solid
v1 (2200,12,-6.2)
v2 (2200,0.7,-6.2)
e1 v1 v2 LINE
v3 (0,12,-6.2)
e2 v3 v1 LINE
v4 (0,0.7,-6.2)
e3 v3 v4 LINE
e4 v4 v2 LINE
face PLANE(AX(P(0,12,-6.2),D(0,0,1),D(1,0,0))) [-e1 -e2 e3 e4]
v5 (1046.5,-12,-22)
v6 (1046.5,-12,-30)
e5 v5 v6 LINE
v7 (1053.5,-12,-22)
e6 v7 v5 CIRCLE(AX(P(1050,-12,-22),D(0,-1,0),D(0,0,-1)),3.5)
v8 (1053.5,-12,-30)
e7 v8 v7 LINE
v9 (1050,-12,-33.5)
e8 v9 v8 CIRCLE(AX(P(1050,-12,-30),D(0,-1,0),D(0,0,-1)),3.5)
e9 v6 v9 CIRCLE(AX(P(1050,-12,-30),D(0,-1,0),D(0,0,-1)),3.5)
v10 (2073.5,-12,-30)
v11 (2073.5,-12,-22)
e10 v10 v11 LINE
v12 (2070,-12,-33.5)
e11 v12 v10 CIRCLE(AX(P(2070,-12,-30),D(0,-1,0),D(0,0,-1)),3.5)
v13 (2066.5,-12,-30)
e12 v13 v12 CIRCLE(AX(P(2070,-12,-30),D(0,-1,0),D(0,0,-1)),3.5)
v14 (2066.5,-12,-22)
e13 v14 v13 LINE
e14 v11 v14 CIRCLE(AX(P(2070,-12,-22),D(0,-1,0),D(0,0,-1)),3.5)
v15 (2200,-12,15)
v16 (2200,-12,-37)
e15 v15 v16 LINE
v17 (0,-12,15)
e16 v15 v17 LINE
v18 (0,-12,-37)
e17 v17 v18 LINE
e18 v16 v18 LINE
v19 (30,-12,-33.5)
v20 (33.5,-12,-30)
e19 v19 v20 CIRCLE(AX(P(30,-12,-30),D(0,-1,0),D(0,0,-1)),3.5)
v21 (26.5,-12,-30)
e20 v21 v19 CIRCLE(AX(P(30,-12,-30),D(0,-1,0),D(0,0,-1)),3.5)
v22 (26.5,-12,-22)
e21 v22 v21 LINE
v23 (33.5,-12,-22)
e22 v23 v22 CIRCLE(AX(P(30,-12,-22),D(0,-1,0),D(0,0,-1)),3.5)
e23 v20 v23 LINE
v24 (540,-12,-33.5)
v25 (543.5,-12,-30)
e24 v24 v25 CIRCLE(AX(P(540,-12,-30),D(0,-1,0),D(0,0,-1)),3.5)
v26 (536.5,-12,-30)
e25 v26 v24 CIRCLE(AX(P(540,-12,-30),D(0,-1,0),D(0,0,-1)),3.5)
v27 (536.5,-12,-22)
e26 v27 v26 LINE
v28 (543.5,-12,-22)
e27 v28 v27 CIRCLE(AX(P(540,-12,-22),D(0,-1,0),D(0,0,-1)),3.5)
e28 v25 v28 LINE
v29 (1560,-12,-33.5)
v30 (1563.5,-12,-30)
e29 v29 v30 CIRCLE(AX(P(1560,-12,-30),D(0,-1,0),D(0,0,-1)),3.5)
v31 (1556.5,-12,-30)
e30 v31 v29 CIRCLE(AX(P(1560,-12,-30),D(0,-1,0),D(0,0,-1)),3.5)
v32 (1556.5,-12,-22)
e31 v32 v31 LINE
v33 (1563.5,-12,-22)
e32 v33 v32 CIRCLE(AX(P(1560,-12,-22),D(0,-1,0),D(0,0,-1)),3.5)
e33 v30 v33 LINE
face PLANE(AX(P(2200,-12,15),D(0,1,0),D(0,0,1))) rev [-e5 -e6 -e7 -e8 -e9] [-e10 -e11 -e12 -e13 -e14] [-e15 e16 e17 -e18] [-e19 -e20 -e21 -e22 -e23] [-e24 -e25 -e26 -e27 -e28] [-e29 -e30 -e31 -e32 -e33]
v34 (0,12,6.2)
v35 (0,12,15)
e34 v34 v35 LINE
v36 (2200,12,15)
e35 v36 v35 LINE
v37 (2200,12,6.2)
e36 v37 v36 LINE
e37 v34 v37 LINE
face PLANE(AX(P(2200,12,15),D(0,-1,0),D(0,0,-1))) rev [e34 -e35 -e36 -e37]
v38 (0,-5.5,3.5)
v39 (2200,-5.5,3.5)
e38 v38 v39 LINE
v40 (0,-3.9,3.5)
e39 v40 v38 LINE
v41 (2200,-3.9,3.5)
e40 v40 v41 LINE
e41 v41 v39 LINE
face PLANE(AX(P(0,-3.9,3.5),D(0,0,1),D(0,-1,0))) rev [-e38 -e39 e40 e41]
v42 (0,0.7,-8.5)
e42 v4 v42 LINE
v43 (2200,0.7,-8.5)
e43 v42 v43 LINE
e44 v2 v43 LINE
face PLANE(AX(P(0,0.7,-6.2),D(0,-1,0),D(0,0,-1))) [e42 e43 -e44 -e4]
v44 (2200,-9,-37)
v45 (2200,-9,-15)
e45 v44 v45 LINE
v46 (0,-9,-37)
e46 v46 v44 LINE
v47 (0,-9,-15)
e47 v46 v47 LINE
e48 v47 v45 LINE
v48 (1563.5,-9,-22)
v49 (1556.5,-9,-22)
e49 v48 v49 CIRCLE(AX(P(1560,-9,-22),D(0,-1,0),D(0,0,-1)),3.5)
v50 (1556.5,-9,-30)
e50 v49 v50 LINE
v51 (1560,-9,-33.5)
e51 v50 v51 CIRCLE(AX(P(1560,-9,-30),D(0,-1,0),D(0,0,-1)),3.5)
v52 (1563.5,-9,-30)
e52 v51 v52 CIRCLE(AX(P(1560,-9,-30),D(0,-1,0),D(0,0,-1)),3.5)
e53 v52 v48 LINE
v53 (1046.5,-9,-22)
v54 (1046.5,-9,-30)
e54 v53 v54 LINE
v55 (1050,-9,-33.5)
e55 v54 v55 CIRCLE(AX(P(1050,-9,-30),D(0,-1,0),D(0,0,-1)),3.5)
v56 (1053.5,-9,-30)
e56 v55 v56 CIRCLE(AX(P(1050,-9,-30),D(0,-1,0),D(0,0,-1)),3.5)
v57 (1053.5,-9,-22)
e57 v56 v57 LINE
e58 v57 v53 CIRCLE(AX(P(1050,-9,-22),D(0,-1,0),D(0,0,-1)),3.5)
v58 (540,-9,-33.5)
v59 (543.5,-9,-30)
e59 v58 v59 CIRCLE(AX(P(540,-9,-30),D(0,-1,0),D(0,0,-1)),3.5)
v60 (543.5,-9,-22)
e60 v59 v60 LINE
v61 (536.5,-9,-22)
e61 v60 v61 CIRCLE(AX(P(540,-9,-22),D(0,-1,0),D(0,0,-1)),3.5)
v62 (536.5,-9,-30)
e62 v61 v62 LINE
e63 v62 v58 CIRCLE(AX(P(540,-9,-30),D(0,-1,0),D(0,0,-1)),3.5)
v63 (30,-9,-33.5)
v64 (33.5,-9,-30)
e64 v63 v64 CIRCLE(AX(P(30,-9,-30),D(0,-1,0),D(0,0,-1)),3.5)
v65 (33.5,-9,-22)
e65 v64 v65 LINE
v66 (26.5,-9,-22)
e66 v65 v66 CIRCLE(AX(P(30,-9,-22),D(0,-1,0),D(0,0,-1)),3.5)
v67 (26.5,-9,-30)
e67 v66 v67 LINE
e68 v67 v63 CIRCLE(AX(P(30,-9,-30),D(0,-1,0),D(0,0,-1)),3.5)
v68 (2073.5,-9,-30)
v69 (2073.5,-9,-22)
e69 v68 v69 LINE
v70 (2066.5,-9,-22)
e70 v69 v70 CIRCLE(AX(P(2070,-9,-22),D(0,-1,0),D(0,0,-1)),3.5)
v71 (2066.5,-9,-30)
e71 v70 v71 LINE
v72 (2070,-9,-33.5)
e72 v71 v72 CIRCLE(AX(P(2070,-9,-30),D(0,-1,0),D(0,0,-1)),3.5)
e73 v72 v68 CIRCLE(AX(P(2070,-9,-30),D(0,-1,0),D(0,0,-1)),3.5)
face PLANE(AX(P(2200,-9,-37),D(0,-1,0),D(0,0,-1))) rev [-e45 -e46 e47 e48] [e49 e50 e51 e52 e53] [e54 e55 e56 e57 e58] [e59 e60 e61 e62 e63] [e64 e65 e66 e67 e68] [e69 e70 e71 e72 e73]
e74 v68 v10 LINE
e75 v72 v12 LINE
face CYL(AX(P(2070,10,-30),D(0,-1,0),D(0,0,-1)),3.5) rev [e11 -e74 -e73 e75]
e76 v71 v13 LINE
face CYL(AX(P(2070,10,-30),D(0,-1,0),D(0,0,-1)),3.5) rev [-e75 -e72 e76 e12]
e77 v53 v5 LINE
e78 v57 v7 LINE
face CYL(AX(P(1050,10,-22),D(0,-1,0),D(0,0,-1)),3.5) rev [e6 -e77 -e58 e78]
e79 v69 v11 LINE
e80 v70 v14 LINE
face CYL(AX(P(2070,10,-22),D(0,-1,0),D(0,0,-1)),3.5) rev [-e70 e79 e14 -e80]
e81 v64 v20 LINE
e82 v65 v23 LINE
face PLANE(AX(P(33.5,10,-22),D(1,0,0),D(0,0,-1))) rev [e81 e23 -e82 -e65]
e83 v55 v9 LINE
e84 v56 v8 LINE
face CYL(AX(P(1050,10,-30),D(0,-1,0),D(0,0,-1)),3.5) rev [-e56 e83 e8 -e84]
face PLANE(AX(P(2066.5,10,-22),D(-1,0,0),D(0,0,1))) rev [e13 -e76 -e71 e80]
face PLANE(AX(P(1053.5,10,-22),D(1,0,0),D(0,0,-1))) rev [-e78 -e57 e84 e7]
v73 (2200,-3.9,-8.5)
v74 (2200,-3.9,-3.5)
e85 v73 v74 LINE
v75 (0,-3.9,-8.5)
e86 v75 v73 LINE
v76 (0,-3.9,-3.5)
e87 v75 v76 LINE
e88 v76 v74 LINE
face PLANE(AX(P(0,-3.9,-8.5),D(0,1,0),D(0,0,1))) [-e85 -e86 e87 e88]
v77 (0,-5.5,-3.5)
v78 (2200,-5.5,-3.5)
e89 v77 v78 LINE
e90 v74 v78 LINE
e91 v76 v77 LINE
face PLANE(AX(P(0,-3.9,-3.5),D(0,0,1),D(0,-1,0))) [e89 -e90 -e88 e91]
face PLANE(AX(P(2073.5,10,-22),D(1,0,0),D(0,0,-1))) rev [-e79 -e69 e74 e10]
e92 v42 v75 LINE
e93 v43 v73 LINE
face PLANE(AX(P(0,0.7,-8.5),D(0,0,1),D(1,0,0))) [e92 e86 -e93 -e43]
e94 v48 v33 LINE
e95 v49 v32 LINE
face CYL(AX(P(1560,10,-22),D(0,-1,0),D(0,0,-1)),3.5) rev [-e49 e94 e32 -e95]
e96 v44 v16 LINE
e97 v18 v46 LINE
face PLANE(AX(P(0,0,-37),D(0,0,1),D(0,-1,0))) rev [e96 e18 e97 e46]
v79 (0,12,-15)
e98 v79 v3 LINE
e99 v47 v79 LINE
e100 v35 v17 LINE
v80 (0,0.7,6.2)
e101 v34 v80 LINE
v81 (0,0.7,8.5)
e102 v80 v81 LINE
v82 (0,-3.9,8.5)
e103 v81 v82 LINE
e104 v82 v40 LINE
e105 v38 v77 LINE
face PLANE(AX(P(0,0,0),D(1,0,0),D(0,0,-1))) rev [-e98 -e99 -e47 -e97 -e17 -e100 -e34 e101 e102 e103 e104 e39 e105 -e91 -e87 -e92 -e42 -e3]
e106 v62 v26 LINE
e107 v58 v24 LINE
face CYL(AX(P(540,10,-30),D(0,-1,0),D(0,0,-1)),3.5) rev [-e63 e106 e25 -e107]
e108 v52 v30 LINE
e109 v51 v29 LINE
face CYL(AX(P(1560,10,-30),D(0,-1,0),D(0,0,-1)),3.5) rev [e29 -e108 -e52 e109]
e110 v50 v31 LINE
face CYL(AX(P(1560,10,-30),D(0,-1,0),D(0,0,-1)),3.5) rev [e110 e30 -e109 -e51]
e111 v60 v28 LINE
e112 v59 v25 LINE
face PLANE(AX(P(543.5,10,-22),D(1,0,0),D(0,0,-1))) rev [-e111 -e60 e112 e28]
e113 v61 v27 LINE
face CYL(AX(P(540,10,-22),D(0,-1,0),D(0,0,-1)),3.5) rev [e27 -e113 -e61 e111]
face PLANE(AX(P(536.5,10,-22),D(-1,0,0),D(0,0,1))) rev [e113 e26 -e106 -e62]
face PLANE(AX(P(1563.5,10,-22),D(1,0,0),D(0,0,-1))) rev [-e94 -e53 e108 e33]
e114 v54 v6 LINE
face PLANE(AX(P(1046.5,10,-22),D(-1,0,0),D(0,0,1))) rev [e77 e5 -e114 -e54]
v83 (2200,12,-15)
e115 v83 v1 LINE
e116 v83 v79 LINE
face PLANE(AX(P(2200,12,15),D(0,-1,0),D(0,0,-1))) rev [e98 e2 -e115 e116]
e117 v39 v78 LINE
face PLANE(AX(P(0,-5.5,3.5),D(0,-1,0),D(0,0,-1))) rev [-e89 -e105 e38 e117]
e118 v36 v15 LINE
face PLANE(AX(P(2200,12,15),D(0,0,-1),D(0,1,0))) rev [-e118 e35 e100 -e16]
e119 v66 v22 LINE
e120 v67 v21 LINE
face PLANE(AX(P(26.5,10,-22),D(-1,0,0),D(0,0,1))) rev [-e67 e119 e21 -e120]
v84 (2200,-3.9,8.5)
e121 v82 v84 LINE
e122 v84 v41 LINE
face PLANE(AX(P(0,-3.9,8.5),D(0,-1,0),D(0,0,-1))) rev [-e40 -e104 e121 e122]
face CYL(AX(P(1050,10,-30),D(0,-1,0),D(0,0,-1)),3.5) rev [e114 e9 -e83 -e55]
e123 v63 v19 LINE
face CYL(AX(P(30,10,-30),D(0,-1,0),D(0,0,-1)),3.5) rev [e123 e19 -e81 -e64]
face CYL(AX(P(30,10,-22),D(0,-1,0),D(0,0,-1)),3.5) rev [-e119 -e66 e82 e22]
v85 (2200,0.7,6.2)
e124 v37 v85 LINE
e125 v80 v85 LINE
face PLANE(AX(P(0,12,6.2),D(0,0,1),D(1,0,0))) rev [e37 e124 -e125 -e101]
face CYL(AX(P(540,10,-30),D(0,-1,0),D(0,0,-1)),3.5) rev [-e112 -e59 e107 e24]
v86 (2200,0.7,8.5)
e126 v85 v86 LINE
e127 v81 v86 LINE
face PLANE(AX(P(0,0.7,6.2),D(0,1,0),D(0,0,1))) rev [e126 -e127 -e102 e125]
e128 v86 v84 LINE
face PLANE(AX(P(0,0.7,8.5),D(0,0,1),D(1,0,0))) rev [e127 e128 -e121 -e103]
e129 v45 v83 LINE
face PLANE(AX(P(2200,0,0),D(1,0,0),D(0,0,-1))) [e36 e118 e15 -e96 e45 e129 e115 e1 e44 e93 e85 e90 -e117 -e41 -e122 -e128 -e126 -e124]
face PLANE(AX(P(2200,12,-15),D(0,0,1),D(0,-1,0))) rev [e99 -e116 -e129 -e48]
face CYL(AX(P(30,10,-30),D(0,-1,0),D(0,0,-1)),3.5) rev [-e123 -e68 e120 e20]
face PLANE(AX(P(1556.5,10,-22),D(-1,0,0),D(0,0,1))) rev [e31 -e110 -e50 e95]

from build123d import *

# Parameters (mm, degrees)
SKETCH_1_W             = 30
SKETCH_1_H             = 24
EXTRUDE_1_DEPTH        = 2200
CUT_EXTRUDE_1_DEPTH    = 2201.083862038
SKETCH_5_W             = 2200
SKETCH_5_H             = 3
EXTRUDE_2_DEPTH        = 22
CUT_EXTRUDE_2_DEPTH    = 22
PATTERN_LINEAR_1_COUNT = 6
PATTERN_LINEAR_1_PITCH = 510


with BuildPart() as part:
    # 草图1 → 凸台-拉伸1 (new body)
    with BuildSketch(Plane(origin=(0, 0, 0), x_dir=(0, 0, -1), z_dir=(1, 0, 0))):
        Rectangle(SKETCH_1_W, SKETCH_1_H)
    extrude(amount=EXTRUDE_1_DEPTH)

    # 草图2 → 切除-拉伸1 (cut, through all)
    with BuildSketch(Plane(origin=(2200, 0, 0), x_dir=(0, 0, -1), z_dir=(1, 0, 0))):
        Polygon((-6.2, 12), (-6.2, 0.7), (-8.5, 0.7), (-8.5, -3.9), (-3.5, -3.9), (-3.5, -5.5), (3.5, -5.5), (3.5, -3.9), (8.5, -3.9), (8.5, 0.7), (6.2, 0.7), (6.2, 12), align=None)
    extrude(amount=-CUT_EXTRUDE_1_DEPTH, mode=Mode.SUBTRACT)

    # 草图5 → 凸台-拉伸2 (add)
    with BuildSketch(Plane(origin=(0, 0, -15), x_dir=(-1, 0, 0), z_dir=(0, 0, -1))):
        with Locations((-1100, -10.5)):
            Rectangle(SKETCH_5_W, SKETCH_5_H)
    extrude(amount=EXTRUDE_2_DEPTH)

    # 草图6 → 切除-拉伸2 (cut)
    with BuildSketch(Plane.XZ.offset(12)):
        with BuildLine():
            Line((33.5, -22), (33.5, -30))
            ThreePointArc((33.5, -30), (30, -33.5), (26.5, -30))
            Line((26.5, -30), (26.5, -22))
            ThreePointArc((26.5, -22), (30, -18.5), (33.5, -22))
        make_face()
    cut_extrude_2 = extrude(amount=-CUT_EXTRUDE_2_DEPTH, mode=Mode.SUBTRACT)

    # 阵列(线性)1: 切除-拉伸2 ×6
    with Locations(*[(i * PATTERN_LINEAR_1_PITCH, 0, 0) for i in range(1, PATTERN_LINEAR_1_COUNT)]):
        add(cut_extrude_2, mode=Mode.SUBTRACT)


solid = part.part
